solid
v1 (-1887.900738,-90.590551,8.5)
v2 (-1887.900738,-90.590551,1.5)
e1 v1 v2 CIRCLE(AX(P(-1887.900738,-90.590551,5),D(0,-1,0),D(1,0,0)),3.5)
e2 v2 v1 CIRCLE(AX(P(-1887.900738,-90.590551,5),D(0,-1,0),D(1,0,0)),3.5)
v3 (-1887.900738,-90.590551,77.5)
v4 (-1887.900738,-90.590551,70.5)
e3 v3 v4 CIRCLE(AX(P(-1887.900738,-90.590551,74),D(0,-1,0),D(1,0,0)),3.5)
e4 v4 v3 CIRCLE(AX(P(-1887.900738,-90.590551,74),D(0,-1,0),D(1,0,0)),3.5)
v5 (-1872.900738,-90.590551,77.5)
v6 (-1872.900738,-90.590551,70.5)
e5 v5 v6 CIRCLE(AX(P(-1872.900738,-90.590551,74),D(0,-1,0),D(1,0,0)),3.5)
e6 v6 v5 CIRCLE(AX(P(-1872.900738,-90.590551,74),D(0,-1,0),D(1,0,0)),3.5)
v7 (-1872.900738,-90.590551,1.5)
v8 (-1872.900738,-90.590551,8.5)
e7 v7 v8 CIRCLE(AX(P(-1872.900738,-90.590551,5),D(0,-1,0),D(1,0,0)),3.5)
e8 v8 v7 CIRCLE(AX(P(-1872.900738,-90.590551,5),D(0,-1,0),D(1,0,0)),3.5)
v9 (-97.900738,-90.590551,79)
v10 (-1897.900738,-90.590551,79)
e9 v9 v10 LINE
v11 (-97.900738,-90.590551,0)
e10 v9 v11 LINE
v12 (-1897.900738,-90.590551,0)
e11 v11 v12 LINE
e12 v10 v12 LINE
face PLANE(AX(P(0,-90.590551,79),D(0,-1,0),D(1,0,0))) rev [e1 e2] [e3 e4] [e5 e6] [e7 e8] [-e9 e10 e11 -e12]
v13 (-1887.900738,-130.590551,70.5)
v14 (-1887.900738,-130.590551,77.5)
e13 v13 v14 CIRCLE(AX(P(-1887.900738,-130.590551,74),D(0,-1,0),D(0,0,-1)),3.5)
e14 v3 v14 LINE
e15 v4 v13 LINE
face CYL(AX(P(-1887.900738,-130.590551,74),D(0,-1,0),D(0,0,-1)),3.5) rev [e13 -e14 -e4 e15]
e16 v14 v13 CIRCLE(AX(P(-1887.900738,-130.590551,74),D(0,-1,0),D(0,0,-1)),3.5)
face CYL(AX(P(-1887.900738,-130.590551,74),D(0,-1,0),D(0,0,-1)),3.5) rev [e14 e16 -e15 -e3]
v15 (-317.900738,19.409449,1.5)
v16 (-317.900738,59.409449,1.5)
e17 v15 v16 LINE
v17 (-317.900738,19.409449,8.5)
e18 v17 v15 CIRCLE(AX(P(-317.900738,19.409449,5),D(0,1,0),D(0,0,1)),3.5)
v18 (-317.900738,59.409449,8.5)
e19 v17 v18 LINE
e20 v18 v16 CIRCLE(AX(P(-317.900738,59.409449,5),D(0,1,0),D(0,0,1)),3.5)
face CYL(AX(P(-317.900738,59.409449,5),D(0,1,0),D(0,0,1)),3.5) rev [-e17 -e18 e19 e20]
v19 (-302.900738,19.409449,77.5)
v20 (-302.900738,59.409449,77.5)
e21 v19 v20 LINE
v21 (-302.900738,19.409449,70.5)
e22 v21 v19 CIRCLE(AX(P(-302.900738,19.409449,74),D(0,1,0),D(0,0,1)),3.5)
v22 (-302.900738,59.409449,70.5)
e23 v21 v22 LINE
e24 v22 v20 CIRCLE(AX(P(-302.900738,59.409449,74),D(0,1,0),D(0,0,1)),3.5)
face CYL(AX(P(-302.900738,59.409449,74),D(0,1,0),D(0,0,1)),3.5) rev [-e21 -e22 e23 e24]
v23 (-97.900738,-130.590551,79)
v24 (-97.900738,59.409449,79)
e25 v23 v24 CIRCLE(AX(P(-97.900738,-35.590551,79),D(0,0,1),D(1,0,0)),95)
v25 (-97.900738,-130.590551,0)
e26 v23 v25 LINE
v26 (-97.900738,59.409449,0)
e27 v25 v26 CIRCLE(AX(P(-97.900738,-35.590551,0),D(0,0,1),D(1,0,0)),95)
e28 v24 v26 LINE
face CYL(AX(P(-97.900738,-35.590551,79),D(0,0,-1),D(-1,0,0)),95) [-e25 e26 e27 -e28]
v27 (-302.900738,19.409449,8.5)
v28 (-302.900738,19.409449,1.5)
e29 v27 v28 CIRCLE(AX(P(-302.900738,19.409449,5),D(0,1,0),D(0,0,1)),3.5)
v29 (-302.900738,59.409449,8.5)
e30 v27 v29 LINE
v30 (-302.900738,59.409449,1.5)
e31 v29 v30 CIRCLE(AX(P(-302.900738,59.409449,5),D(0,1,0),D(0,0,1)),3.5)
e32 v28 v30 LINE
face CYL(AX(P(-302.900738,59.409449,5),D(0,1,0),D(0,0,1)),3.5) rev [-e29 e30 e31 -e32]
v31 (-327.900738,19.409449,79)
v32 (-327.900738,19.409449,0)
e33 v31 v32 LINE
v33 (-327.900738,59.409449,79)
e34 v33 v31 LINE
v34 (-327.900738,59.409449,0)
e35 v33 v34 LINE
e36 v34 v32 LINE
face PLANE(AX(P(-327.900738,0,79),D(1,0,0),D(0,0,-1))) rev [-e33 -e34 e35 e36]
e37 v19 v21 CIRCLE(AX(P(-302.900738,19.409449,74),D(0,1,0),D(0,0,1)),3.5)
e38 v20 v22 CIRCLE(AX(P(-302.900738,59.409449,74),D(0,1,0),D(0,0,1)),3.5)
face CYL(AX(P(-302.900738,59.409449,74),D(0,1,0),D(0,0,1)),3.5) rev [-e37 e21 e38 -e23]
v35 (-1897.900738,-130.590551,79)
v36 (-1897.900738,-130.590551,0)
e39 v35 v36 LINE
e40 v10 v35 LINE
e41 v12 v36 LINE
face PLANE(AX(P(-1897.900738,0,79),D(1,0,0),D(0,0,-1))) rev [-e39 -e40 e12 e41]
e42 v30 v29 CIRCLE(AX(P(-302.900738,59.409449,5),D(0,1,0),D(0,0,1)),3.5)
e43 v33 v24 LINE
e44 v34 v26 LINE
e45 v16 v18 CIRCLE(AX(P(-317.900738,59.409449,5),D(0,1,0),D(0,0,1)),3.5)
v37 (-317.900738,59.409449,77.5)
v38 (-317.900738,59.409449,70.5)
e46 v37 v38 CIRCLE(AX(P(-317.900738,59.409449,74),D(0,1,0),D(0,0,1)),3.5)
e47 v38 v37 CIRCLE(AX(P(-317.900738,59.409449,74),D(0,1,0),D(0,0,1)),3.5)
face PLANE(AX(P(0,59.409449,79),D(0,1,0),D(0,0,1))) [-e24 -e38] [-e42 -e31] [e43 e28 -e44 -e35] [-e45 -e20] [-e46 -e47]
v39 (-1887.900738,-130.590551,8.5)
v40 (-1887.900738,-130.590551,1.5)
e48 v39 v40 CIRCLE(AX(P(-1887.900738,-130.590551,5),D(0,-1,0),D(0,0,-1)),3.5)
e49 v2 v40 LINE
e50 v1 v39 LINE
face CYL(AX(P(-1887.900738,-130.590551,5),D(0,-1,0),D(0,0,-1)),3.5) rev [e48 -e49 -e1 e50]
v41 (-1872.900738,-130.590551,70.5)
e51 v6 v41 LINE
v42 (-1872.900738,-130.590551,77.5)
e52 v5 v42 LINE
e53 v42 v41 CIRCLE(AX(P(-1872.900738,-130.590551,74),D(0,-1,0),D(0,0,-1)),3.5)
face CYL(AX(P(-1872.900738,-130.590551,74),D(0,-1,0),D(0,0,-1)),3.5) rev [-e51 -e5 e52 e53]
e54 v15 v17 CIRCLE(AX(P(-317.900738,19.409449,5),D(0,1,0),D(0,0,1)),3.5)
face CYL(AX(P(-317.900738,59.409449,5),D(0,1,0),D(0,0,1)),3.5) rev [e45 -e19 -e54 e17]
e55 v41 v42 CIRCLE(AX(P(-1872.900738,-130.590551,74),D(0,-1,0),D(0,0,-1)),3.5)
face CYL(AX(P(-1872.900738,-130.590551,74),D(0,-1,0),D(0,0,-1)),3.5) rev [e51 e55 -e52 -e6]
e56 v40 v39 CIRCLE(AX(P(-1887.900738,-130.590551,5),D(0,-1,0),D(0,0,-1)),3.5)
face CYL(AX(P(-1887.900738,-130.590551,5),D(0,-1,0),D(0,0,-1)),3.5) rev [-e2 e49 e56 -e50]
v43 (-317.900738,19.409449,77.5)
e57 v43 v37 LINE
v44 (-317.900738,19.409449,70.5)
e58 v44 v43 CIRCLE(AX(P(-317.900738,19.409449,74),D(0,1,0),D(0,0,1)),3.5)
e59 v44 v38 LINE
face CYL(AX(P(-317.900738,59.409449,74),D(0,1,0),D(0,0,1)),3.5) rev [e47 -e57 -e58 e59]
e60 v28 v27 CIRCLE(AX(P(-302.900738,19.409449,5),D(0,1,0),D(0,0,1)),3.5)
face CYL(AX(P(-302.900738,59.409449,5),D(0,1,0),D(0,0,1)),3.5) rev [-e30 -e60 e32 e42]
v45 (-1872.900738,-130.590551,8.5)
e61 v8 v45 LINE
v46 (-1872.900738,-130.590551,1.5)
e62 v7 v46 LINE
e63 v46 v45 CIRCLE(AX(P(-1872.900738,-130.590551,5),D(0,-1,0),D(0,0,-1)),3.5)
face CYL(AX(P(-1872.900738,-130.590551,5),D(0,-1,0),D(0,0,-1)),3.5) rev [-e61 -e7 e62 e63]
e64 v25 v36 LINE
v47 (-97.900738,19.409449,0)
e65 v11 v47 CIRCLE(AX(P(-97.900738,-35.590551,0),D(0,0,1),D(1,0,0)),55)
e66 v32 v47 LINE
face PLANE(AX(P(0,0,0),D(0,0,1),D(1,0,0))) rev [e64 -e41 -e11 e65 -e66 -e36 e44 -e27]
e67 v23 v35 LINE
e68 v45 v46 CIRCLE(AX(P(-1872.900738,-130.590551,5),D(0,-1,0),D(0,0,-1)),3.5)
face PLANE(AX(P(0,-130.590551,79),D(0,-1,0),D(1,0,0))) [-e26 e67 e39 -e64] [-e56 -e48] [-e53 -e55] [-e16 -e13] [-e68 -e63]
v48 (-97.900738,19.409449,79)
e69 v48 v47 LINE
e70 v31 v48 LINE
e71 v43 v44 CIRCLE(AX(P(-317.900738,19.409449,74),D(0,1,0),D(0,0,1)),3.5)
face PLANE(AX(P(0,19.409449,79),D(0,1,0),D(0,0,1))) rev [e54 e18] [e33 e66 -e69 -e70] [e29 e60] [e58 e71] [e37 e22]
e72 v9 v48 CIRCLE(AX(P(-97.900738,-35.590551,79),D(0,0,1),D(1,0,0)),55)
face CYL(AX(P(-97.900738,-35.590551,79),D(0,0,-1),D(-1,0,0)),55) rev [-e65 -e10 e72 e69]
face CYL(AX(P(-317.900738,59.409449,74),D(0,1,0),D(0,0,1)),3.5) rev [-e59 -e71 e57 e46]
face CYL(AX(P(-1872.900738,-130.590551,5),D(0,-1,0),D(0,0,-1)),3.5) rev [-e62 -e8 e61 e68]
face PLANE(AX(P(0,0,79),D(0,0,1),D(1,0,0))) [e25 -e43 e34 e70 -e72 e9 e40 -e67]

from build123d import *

# Parameters (mm, degrees)
EXTRUDE_1_DEPTH           = 79
HOLE_WIZARD_7_0_7_1_D     = 7
HOLE_WIZARD_7_0_7_2_D     = 7
HOLE_WIZARD_7_0_7_2_DEPTH = 40


with BuildPart() as part:
    # 草图1 → 凸台-拉伸1 (new body)
    with BuildSketch(Plane.XY):
        with BuildLine():
            Line((-327.90073838, 19.409448819), (-97.90073838, 19.409448819))
            ThreePointArc((-97.90073838, 19.409448819), (-42.90073838, -35.590551181), (-97.90073838, -90.590551181))
            Line((-97.90073838, -90.590551181), (-1897.90073838, -90.590551181))
            Line((-1897.90073838, -90.590551181), (-1897.90073838, -130.590551181))
            Line((-1897.90073838, -130.590551181), (-97.90073838, -130.590551181))
            ThreePointArc((-97.90073838, -130.590551181), (-2.90073838, -35.590551181), (-97.90073838, 59.409448819))
            Line((-97.90073838, 59.409448819), (-327.90073838, 59.409448819))
            Line((-327.90073838, 59.409448819), (-327.90073838, 19.409448819))
        make_face()
    extrude(amount=EXTRUDE_1_DEPTH)

    # Ø7.0 (7) 直径孔1 (through all)
    with Locations(Plane(origin=(0, -130.590551181, 0), x_dir=(-1, 0, 0), z_dir=(0, -1, 0))):
        with Locations((1872.90073838, -5), (1887.90073838, -5), (1872.90073838, -74), (1887.90073838, -74)):
            Hole(HOLE_WIZARD_7_0_7_1_D / 2)

    # Ø7.0 (7) 直径孔2
    with Locations(Plane(origin=(0, 59.409448819, 0), x_dir=(1, 0, 0), z_dir=(0, 1, 0))):
        with Locations((-317.90073838, -5), (-302.90073838, -5), (-317.90073838, -74), (-302.90073838, -74)):
            Hole(HOLE_WIZARD_7_0_7_2_D / 2, depth=HOLE_WIZARD_7_0_7_2_DEPTH)


solid = part.part
